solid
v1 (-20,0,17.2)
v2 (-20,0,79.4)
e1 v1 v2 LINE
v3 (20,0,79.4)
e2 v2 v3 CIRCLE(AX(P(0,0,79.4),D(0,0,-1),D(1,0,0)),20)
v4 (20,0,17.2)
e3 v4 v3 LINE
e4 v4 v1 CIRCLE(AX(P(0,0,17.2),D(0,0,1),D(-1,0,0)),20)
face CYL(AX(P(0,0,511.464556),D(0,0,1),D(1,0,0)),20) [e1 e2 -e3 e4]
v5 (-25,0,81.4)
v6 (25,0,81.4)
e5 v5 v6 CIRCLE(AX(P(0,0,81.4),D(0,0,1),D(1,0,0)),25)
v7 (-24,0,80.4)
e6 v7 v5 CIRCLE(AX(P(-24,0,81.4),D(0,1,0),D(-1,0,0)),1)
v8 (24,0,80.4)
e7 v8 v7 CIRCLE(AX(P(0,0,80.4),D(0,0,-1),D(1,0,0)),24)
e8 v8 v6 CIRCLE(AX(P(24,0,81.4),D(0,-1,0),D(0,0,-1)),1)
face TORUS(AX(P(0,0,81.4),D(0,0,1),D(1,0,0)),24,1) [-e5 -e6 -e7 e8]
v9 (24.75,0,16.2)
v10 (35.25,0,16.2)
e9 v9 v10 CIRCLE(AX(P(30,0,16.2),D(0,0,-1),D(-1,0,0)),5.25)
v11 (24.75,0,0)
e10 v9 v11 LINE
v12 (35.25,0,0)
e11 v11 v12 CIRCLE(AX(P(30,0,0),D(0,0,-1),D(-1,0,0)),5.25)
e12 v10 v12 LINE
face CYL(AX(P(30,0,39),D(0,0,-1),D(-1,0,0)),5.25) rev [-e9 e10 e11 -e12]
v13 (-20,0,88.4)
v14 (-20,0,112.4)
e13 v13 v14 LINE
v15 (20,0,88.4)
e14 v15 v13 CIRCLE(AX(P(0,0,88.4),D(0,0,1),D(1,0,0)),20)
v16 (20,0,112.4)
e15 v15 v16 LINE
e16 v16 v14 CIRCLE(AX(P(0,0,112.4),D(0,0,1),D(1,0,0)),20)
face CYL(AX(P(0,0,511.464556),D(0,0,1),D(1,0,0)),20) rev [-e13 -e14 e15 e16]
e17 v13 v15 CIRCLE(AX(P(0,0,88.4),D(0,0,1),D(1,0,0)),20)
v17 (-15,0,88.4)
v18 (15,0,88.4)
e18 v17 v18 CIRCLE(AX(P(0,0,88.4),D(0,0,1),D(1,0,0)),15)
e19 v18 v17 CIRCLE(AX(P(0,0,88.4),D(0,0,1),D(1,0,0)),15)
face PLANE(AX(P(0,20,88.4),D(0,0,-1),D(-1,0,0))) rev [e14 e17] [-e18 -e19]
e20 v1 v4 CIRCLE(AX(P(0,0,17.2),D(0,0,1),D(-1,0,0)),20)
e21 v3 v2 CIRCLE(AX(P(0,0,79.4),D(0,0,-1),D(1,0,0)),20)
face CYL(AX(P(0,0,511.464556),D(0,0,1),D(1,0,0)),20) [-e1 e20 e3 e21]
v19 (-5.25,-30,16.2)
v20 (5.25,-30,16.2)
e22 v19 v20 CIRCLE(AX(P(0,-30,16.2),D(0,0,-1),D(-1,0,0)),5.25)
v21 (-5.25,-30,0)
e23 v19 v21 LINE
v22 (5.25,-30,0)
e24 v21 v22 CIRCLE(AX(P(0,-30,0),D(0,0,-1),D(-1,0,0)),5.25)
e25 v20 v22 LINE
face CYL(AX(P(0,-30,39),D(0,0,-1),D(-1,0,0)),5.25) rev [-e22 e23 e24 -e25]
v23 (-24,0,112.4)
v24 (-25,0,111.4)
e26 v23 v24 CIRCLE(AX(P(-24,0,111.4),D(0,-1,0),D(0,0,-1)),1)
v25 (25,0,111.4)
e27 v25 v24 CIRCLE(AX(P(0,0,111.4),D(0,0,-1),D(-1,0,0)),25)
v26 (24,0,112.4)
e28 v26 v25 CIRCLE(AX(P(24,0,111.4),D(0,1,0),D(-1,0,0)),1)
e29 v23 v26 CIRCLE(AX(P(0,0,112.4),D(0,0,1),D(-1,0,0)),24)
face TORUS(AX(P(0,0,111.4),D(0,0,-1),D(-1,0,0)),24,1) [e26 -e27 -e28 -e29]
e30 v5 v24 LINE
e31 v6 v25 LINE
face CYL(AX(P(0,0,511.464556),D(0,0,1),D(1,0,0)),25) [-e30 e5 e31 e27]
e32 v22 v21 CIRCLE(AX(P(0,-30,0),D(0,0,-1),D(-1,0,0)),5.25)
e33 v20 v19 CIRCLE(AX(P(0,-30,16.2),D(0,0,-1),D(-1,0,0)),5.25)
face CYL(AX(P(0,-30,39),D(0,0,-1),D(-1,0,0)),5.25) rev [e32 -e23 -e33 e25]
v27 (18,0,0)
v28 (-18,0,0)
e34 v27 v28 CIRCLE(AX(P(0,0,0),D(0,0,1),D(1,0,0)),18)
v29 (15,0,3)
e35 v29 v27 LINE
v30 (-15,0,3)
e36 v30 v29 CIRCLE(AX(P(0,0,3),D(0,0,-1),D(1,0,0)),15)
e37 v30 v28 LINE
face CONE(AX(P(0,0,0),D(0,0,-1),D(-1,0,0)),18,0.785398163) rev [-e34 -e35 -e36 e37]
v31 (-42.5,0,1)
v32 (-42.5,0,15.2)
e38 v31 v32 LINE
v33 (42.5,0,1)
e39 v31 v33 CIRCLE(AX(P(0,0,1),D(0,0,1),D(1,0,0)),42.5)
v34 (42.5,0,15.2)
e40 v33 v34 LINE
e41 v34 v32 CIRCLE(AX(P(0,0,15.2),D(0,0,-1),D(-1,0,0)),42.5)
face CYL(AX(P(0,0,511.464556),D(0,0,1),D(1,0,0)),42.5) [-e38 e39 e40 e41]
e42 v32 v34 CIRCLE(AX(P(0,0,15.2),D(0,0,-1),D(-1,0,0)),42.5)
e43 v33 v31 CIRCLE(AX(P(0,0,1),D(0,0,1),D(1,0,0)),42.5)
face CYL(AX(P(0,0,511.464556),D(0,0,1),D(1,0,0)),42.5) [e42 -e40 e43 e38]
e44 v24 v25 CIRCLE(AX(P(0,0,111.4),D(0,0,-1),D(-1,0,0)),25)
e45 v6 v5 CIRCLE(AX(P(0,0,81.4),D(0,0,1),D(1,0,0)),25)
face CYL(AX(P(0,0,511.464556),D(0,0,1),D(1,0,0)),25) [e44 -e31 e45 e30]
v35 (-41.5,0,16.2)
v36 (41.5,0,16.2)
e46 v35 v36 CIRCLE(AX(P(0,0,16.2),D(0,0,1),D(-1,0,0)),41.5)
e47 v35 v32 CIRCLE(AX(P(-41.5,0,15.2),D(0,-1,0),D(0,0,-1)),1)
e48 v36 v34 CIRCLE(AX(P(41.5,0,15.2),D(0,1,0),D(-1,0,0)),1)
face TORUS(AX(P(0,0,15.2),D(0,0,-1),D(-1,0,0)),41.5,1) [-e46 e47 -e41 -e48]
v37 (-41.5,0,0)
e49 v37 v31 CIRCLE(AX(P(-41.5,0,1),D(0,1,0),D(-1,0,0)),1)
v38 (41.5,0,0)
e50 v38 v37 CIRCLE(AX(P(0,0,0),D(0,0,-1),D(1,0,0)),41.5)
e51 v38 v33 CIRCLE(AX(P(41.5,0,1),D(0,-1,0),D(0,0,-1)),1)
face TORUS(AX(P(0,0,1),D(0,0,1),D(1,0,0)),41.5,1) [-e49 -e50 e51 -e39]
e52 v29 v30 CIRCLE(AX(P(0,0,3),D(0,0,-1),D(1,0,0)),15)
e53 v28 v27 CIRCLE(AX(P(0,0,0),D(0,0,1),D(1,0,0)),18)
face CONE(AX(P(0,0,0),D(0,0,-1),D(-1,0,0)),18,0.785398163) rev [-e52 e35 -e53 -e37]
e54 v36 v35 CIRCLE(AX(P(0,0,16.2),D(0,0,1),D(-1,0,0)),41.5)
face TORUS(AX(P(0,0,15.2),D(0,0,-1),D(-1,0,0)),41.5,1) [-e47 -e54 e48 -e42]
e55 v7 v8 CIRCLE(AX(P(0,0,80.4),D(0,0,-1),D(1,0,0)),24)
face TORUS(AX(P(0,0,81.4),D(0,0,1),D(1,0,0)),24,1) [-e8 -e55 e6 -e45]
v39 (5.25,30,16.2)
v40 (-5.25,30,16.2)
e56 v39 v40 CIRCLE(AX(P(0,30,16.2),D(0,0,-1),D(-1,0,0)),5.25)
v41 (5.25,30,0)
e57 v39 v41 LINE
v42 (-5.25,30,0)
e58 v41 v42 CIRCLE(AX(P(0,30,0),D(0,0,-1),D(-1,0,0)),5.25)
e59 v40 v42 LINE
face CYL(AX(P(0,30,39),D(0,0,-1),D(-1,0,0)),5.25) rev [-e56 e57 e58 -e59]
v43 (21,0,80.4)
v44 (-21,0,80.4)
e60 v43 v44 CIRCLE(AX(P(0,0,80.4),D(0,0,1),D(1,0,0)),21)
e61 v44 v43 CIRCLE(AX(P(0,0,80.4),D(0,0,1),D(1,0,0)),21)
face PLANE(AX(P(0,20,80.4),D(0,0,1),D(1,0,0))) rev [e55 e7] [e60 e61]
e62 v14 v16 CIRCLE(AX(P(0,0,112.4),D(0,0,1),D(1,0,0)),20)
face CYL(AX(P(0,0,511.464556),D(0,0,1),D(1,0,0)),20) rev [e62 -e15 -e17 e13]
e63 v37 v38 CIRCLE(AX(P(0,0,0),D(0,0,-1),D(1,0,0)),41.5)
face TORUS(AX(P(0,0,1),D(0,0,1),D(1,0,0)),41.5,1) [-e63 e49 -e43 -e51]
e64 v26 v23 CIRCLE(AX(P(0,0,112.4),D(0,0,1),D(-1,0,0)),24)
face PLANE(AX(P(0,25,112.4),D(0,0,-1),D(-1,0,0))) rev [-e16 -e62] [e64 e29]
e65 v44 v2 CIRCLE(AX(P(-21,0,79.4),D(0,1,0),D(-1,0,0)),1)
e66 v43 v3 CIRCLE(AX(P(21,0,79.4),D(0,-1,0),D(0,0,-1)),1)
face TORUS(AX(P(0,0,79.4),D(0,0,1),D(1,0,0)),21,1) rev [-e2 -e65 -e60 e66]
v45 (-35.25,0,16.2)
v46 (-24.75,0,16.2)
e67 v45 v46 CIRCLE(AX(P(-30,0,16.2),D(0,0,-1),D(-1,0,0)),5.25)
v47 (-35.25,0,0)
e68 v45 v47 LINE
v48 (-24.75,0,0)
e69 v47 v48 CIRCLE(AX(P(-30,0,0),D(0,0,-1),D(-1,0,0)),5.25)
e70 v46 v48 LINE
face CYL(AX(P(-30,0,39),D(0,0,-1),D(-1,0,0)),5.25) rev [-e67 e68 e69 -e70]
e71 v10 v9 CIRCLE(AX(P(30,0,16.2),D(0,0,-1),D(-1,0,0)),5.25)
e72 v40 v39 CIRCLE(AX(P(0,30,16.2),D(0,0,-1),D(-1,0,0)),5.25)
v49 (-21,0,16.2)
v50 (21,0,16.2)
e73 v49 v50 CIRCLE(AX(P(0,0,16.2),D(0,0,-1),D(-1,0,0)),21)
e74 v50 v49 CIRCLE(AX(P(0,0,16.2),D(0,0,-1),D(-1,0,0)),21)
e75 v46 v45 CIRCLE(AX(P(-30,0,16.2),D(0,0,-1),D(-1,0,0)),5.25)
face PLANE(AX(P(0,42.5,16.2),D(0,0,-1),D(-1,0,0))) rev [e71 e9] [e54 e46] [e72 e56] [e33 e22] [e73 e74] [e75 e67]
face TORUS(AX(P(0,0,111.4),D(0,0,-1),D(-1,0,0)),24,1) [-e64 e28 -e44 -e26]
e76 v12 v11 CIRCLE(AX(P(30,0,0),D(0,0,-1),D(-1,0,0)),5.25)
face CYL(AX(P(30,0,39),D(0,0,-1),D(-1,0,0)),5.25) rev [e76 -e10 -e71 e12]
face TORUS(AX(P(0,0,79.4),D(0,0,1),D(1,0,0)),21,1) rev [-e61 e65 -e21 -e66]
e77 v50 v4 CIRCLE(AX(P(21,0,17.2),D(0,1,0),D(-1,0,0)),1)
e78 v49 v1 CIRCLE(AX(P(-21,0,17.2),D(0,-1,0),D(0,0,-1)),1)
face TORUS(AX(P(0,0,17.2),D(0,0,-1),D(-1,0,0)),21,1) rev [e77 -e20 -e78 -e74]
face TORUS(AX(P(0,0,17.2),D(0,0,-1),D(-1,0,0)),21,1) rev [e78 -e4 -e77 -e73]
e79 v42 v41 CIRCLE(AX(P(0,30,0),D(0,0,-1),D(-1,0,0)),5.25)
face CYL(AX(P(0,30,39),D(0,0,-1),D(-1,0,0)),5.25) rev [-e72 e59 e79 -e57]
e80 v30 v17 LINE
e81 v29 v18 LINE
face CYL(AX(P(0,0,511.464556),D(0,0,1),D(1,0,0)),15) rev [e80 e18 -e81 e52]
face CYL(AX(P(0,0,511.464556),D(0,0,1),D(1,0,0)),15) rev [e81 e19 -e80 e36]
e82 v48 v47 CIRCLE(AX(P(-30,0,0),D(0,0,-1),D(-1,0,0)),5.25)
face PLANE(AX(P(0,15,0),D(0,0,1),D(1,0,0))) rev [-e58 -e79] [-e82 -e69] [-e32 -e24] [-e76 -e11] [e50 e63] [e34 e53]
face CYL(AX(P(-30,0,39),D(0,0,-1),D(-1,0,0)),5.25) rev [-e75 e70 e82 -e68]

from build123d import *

# Parameters (mm, degrees)
FLANGE_HOLES_SKETCH_R      = 5.25
FLANGE_HOLES_4X_10_5_DEPTH = 39
CHAMFER_3X45_SIZE          = 3
FILLET_R1_R                = 1


with BuildPart() as part:
    # Bush Profile Sketch → Flanged Bush Body (revolve)
    with BuildSketch(Plane(origin=(0, 0, 0), x_dir=(0, 0, -1), z_dir=(1, 0, 0)), mode=Mode.PRIVATE) as flanged_bush_body_sk:
        Polygon((0, 15), (0, 42.5), (-16.2, 42.5), (-16.2, 20), (-80.4, 20), (-80.4, 25), (-112.4, 25), (-112.4, 20), (-88.4, 20), (-88.4, 15), align=None)
    revolve(flanged_bush_body_sk.sketch.rotate(Axis((0, 0, 511.464555616), (0, 0, -1)), 90), axis=Axis((0, 0, 511.464555616), (0, 0, -1)))

    # Flange Holes Sketch → Flange Holes 4xØ10.5 (cut)
    with BuildSketch(Plane(origin=(0, 0, 0), x_dir=(-1, 0, 0), z_dir=(0, 0, -1))):
        with Locations((0, 30)):
            Circle(FLANGE_HOLES_SKETCH_R)
        with Locations((30, 0)):
            Circle(FLANGE_HOLES_SKETCH_R)
        with Locations((0, -30)):
            Circle(FLANGE_HOLES_SKETCH_R)
        with Locations((-30, 0)):
            Circle(FLANGE_HOLES_SKETCH_R)
    extrude(amount=-FLANGE_HOLES_4X_10_5_DEPTH, mode=Mode.SUBTRACT)

    # Chamfer 3x45
    chamfer_3x45_edges = [part.edges().sort_by_distance(p)[0] for p in [
        (-15, 0, 0),
    ]]
    chamfer(chamfer_3x45_edges, length=CHAMFER_3X45_SIZE)

    # Fillet R1
    fillet_r1_edges = [part.edges().sort_by_distance(p)[0] for p in [
        (-20, 0, 80.4),
        (-20, 0, 16.2),
        (-42.5, 0, 16.2),
        (-42.5, 0, 0),
        (-25, 0, 112.4),
        (-25, 0, 80.4),
    ]]
    fillet(fillet_r1_edges, radius=FILLET_R1_R)


solid = part.part
